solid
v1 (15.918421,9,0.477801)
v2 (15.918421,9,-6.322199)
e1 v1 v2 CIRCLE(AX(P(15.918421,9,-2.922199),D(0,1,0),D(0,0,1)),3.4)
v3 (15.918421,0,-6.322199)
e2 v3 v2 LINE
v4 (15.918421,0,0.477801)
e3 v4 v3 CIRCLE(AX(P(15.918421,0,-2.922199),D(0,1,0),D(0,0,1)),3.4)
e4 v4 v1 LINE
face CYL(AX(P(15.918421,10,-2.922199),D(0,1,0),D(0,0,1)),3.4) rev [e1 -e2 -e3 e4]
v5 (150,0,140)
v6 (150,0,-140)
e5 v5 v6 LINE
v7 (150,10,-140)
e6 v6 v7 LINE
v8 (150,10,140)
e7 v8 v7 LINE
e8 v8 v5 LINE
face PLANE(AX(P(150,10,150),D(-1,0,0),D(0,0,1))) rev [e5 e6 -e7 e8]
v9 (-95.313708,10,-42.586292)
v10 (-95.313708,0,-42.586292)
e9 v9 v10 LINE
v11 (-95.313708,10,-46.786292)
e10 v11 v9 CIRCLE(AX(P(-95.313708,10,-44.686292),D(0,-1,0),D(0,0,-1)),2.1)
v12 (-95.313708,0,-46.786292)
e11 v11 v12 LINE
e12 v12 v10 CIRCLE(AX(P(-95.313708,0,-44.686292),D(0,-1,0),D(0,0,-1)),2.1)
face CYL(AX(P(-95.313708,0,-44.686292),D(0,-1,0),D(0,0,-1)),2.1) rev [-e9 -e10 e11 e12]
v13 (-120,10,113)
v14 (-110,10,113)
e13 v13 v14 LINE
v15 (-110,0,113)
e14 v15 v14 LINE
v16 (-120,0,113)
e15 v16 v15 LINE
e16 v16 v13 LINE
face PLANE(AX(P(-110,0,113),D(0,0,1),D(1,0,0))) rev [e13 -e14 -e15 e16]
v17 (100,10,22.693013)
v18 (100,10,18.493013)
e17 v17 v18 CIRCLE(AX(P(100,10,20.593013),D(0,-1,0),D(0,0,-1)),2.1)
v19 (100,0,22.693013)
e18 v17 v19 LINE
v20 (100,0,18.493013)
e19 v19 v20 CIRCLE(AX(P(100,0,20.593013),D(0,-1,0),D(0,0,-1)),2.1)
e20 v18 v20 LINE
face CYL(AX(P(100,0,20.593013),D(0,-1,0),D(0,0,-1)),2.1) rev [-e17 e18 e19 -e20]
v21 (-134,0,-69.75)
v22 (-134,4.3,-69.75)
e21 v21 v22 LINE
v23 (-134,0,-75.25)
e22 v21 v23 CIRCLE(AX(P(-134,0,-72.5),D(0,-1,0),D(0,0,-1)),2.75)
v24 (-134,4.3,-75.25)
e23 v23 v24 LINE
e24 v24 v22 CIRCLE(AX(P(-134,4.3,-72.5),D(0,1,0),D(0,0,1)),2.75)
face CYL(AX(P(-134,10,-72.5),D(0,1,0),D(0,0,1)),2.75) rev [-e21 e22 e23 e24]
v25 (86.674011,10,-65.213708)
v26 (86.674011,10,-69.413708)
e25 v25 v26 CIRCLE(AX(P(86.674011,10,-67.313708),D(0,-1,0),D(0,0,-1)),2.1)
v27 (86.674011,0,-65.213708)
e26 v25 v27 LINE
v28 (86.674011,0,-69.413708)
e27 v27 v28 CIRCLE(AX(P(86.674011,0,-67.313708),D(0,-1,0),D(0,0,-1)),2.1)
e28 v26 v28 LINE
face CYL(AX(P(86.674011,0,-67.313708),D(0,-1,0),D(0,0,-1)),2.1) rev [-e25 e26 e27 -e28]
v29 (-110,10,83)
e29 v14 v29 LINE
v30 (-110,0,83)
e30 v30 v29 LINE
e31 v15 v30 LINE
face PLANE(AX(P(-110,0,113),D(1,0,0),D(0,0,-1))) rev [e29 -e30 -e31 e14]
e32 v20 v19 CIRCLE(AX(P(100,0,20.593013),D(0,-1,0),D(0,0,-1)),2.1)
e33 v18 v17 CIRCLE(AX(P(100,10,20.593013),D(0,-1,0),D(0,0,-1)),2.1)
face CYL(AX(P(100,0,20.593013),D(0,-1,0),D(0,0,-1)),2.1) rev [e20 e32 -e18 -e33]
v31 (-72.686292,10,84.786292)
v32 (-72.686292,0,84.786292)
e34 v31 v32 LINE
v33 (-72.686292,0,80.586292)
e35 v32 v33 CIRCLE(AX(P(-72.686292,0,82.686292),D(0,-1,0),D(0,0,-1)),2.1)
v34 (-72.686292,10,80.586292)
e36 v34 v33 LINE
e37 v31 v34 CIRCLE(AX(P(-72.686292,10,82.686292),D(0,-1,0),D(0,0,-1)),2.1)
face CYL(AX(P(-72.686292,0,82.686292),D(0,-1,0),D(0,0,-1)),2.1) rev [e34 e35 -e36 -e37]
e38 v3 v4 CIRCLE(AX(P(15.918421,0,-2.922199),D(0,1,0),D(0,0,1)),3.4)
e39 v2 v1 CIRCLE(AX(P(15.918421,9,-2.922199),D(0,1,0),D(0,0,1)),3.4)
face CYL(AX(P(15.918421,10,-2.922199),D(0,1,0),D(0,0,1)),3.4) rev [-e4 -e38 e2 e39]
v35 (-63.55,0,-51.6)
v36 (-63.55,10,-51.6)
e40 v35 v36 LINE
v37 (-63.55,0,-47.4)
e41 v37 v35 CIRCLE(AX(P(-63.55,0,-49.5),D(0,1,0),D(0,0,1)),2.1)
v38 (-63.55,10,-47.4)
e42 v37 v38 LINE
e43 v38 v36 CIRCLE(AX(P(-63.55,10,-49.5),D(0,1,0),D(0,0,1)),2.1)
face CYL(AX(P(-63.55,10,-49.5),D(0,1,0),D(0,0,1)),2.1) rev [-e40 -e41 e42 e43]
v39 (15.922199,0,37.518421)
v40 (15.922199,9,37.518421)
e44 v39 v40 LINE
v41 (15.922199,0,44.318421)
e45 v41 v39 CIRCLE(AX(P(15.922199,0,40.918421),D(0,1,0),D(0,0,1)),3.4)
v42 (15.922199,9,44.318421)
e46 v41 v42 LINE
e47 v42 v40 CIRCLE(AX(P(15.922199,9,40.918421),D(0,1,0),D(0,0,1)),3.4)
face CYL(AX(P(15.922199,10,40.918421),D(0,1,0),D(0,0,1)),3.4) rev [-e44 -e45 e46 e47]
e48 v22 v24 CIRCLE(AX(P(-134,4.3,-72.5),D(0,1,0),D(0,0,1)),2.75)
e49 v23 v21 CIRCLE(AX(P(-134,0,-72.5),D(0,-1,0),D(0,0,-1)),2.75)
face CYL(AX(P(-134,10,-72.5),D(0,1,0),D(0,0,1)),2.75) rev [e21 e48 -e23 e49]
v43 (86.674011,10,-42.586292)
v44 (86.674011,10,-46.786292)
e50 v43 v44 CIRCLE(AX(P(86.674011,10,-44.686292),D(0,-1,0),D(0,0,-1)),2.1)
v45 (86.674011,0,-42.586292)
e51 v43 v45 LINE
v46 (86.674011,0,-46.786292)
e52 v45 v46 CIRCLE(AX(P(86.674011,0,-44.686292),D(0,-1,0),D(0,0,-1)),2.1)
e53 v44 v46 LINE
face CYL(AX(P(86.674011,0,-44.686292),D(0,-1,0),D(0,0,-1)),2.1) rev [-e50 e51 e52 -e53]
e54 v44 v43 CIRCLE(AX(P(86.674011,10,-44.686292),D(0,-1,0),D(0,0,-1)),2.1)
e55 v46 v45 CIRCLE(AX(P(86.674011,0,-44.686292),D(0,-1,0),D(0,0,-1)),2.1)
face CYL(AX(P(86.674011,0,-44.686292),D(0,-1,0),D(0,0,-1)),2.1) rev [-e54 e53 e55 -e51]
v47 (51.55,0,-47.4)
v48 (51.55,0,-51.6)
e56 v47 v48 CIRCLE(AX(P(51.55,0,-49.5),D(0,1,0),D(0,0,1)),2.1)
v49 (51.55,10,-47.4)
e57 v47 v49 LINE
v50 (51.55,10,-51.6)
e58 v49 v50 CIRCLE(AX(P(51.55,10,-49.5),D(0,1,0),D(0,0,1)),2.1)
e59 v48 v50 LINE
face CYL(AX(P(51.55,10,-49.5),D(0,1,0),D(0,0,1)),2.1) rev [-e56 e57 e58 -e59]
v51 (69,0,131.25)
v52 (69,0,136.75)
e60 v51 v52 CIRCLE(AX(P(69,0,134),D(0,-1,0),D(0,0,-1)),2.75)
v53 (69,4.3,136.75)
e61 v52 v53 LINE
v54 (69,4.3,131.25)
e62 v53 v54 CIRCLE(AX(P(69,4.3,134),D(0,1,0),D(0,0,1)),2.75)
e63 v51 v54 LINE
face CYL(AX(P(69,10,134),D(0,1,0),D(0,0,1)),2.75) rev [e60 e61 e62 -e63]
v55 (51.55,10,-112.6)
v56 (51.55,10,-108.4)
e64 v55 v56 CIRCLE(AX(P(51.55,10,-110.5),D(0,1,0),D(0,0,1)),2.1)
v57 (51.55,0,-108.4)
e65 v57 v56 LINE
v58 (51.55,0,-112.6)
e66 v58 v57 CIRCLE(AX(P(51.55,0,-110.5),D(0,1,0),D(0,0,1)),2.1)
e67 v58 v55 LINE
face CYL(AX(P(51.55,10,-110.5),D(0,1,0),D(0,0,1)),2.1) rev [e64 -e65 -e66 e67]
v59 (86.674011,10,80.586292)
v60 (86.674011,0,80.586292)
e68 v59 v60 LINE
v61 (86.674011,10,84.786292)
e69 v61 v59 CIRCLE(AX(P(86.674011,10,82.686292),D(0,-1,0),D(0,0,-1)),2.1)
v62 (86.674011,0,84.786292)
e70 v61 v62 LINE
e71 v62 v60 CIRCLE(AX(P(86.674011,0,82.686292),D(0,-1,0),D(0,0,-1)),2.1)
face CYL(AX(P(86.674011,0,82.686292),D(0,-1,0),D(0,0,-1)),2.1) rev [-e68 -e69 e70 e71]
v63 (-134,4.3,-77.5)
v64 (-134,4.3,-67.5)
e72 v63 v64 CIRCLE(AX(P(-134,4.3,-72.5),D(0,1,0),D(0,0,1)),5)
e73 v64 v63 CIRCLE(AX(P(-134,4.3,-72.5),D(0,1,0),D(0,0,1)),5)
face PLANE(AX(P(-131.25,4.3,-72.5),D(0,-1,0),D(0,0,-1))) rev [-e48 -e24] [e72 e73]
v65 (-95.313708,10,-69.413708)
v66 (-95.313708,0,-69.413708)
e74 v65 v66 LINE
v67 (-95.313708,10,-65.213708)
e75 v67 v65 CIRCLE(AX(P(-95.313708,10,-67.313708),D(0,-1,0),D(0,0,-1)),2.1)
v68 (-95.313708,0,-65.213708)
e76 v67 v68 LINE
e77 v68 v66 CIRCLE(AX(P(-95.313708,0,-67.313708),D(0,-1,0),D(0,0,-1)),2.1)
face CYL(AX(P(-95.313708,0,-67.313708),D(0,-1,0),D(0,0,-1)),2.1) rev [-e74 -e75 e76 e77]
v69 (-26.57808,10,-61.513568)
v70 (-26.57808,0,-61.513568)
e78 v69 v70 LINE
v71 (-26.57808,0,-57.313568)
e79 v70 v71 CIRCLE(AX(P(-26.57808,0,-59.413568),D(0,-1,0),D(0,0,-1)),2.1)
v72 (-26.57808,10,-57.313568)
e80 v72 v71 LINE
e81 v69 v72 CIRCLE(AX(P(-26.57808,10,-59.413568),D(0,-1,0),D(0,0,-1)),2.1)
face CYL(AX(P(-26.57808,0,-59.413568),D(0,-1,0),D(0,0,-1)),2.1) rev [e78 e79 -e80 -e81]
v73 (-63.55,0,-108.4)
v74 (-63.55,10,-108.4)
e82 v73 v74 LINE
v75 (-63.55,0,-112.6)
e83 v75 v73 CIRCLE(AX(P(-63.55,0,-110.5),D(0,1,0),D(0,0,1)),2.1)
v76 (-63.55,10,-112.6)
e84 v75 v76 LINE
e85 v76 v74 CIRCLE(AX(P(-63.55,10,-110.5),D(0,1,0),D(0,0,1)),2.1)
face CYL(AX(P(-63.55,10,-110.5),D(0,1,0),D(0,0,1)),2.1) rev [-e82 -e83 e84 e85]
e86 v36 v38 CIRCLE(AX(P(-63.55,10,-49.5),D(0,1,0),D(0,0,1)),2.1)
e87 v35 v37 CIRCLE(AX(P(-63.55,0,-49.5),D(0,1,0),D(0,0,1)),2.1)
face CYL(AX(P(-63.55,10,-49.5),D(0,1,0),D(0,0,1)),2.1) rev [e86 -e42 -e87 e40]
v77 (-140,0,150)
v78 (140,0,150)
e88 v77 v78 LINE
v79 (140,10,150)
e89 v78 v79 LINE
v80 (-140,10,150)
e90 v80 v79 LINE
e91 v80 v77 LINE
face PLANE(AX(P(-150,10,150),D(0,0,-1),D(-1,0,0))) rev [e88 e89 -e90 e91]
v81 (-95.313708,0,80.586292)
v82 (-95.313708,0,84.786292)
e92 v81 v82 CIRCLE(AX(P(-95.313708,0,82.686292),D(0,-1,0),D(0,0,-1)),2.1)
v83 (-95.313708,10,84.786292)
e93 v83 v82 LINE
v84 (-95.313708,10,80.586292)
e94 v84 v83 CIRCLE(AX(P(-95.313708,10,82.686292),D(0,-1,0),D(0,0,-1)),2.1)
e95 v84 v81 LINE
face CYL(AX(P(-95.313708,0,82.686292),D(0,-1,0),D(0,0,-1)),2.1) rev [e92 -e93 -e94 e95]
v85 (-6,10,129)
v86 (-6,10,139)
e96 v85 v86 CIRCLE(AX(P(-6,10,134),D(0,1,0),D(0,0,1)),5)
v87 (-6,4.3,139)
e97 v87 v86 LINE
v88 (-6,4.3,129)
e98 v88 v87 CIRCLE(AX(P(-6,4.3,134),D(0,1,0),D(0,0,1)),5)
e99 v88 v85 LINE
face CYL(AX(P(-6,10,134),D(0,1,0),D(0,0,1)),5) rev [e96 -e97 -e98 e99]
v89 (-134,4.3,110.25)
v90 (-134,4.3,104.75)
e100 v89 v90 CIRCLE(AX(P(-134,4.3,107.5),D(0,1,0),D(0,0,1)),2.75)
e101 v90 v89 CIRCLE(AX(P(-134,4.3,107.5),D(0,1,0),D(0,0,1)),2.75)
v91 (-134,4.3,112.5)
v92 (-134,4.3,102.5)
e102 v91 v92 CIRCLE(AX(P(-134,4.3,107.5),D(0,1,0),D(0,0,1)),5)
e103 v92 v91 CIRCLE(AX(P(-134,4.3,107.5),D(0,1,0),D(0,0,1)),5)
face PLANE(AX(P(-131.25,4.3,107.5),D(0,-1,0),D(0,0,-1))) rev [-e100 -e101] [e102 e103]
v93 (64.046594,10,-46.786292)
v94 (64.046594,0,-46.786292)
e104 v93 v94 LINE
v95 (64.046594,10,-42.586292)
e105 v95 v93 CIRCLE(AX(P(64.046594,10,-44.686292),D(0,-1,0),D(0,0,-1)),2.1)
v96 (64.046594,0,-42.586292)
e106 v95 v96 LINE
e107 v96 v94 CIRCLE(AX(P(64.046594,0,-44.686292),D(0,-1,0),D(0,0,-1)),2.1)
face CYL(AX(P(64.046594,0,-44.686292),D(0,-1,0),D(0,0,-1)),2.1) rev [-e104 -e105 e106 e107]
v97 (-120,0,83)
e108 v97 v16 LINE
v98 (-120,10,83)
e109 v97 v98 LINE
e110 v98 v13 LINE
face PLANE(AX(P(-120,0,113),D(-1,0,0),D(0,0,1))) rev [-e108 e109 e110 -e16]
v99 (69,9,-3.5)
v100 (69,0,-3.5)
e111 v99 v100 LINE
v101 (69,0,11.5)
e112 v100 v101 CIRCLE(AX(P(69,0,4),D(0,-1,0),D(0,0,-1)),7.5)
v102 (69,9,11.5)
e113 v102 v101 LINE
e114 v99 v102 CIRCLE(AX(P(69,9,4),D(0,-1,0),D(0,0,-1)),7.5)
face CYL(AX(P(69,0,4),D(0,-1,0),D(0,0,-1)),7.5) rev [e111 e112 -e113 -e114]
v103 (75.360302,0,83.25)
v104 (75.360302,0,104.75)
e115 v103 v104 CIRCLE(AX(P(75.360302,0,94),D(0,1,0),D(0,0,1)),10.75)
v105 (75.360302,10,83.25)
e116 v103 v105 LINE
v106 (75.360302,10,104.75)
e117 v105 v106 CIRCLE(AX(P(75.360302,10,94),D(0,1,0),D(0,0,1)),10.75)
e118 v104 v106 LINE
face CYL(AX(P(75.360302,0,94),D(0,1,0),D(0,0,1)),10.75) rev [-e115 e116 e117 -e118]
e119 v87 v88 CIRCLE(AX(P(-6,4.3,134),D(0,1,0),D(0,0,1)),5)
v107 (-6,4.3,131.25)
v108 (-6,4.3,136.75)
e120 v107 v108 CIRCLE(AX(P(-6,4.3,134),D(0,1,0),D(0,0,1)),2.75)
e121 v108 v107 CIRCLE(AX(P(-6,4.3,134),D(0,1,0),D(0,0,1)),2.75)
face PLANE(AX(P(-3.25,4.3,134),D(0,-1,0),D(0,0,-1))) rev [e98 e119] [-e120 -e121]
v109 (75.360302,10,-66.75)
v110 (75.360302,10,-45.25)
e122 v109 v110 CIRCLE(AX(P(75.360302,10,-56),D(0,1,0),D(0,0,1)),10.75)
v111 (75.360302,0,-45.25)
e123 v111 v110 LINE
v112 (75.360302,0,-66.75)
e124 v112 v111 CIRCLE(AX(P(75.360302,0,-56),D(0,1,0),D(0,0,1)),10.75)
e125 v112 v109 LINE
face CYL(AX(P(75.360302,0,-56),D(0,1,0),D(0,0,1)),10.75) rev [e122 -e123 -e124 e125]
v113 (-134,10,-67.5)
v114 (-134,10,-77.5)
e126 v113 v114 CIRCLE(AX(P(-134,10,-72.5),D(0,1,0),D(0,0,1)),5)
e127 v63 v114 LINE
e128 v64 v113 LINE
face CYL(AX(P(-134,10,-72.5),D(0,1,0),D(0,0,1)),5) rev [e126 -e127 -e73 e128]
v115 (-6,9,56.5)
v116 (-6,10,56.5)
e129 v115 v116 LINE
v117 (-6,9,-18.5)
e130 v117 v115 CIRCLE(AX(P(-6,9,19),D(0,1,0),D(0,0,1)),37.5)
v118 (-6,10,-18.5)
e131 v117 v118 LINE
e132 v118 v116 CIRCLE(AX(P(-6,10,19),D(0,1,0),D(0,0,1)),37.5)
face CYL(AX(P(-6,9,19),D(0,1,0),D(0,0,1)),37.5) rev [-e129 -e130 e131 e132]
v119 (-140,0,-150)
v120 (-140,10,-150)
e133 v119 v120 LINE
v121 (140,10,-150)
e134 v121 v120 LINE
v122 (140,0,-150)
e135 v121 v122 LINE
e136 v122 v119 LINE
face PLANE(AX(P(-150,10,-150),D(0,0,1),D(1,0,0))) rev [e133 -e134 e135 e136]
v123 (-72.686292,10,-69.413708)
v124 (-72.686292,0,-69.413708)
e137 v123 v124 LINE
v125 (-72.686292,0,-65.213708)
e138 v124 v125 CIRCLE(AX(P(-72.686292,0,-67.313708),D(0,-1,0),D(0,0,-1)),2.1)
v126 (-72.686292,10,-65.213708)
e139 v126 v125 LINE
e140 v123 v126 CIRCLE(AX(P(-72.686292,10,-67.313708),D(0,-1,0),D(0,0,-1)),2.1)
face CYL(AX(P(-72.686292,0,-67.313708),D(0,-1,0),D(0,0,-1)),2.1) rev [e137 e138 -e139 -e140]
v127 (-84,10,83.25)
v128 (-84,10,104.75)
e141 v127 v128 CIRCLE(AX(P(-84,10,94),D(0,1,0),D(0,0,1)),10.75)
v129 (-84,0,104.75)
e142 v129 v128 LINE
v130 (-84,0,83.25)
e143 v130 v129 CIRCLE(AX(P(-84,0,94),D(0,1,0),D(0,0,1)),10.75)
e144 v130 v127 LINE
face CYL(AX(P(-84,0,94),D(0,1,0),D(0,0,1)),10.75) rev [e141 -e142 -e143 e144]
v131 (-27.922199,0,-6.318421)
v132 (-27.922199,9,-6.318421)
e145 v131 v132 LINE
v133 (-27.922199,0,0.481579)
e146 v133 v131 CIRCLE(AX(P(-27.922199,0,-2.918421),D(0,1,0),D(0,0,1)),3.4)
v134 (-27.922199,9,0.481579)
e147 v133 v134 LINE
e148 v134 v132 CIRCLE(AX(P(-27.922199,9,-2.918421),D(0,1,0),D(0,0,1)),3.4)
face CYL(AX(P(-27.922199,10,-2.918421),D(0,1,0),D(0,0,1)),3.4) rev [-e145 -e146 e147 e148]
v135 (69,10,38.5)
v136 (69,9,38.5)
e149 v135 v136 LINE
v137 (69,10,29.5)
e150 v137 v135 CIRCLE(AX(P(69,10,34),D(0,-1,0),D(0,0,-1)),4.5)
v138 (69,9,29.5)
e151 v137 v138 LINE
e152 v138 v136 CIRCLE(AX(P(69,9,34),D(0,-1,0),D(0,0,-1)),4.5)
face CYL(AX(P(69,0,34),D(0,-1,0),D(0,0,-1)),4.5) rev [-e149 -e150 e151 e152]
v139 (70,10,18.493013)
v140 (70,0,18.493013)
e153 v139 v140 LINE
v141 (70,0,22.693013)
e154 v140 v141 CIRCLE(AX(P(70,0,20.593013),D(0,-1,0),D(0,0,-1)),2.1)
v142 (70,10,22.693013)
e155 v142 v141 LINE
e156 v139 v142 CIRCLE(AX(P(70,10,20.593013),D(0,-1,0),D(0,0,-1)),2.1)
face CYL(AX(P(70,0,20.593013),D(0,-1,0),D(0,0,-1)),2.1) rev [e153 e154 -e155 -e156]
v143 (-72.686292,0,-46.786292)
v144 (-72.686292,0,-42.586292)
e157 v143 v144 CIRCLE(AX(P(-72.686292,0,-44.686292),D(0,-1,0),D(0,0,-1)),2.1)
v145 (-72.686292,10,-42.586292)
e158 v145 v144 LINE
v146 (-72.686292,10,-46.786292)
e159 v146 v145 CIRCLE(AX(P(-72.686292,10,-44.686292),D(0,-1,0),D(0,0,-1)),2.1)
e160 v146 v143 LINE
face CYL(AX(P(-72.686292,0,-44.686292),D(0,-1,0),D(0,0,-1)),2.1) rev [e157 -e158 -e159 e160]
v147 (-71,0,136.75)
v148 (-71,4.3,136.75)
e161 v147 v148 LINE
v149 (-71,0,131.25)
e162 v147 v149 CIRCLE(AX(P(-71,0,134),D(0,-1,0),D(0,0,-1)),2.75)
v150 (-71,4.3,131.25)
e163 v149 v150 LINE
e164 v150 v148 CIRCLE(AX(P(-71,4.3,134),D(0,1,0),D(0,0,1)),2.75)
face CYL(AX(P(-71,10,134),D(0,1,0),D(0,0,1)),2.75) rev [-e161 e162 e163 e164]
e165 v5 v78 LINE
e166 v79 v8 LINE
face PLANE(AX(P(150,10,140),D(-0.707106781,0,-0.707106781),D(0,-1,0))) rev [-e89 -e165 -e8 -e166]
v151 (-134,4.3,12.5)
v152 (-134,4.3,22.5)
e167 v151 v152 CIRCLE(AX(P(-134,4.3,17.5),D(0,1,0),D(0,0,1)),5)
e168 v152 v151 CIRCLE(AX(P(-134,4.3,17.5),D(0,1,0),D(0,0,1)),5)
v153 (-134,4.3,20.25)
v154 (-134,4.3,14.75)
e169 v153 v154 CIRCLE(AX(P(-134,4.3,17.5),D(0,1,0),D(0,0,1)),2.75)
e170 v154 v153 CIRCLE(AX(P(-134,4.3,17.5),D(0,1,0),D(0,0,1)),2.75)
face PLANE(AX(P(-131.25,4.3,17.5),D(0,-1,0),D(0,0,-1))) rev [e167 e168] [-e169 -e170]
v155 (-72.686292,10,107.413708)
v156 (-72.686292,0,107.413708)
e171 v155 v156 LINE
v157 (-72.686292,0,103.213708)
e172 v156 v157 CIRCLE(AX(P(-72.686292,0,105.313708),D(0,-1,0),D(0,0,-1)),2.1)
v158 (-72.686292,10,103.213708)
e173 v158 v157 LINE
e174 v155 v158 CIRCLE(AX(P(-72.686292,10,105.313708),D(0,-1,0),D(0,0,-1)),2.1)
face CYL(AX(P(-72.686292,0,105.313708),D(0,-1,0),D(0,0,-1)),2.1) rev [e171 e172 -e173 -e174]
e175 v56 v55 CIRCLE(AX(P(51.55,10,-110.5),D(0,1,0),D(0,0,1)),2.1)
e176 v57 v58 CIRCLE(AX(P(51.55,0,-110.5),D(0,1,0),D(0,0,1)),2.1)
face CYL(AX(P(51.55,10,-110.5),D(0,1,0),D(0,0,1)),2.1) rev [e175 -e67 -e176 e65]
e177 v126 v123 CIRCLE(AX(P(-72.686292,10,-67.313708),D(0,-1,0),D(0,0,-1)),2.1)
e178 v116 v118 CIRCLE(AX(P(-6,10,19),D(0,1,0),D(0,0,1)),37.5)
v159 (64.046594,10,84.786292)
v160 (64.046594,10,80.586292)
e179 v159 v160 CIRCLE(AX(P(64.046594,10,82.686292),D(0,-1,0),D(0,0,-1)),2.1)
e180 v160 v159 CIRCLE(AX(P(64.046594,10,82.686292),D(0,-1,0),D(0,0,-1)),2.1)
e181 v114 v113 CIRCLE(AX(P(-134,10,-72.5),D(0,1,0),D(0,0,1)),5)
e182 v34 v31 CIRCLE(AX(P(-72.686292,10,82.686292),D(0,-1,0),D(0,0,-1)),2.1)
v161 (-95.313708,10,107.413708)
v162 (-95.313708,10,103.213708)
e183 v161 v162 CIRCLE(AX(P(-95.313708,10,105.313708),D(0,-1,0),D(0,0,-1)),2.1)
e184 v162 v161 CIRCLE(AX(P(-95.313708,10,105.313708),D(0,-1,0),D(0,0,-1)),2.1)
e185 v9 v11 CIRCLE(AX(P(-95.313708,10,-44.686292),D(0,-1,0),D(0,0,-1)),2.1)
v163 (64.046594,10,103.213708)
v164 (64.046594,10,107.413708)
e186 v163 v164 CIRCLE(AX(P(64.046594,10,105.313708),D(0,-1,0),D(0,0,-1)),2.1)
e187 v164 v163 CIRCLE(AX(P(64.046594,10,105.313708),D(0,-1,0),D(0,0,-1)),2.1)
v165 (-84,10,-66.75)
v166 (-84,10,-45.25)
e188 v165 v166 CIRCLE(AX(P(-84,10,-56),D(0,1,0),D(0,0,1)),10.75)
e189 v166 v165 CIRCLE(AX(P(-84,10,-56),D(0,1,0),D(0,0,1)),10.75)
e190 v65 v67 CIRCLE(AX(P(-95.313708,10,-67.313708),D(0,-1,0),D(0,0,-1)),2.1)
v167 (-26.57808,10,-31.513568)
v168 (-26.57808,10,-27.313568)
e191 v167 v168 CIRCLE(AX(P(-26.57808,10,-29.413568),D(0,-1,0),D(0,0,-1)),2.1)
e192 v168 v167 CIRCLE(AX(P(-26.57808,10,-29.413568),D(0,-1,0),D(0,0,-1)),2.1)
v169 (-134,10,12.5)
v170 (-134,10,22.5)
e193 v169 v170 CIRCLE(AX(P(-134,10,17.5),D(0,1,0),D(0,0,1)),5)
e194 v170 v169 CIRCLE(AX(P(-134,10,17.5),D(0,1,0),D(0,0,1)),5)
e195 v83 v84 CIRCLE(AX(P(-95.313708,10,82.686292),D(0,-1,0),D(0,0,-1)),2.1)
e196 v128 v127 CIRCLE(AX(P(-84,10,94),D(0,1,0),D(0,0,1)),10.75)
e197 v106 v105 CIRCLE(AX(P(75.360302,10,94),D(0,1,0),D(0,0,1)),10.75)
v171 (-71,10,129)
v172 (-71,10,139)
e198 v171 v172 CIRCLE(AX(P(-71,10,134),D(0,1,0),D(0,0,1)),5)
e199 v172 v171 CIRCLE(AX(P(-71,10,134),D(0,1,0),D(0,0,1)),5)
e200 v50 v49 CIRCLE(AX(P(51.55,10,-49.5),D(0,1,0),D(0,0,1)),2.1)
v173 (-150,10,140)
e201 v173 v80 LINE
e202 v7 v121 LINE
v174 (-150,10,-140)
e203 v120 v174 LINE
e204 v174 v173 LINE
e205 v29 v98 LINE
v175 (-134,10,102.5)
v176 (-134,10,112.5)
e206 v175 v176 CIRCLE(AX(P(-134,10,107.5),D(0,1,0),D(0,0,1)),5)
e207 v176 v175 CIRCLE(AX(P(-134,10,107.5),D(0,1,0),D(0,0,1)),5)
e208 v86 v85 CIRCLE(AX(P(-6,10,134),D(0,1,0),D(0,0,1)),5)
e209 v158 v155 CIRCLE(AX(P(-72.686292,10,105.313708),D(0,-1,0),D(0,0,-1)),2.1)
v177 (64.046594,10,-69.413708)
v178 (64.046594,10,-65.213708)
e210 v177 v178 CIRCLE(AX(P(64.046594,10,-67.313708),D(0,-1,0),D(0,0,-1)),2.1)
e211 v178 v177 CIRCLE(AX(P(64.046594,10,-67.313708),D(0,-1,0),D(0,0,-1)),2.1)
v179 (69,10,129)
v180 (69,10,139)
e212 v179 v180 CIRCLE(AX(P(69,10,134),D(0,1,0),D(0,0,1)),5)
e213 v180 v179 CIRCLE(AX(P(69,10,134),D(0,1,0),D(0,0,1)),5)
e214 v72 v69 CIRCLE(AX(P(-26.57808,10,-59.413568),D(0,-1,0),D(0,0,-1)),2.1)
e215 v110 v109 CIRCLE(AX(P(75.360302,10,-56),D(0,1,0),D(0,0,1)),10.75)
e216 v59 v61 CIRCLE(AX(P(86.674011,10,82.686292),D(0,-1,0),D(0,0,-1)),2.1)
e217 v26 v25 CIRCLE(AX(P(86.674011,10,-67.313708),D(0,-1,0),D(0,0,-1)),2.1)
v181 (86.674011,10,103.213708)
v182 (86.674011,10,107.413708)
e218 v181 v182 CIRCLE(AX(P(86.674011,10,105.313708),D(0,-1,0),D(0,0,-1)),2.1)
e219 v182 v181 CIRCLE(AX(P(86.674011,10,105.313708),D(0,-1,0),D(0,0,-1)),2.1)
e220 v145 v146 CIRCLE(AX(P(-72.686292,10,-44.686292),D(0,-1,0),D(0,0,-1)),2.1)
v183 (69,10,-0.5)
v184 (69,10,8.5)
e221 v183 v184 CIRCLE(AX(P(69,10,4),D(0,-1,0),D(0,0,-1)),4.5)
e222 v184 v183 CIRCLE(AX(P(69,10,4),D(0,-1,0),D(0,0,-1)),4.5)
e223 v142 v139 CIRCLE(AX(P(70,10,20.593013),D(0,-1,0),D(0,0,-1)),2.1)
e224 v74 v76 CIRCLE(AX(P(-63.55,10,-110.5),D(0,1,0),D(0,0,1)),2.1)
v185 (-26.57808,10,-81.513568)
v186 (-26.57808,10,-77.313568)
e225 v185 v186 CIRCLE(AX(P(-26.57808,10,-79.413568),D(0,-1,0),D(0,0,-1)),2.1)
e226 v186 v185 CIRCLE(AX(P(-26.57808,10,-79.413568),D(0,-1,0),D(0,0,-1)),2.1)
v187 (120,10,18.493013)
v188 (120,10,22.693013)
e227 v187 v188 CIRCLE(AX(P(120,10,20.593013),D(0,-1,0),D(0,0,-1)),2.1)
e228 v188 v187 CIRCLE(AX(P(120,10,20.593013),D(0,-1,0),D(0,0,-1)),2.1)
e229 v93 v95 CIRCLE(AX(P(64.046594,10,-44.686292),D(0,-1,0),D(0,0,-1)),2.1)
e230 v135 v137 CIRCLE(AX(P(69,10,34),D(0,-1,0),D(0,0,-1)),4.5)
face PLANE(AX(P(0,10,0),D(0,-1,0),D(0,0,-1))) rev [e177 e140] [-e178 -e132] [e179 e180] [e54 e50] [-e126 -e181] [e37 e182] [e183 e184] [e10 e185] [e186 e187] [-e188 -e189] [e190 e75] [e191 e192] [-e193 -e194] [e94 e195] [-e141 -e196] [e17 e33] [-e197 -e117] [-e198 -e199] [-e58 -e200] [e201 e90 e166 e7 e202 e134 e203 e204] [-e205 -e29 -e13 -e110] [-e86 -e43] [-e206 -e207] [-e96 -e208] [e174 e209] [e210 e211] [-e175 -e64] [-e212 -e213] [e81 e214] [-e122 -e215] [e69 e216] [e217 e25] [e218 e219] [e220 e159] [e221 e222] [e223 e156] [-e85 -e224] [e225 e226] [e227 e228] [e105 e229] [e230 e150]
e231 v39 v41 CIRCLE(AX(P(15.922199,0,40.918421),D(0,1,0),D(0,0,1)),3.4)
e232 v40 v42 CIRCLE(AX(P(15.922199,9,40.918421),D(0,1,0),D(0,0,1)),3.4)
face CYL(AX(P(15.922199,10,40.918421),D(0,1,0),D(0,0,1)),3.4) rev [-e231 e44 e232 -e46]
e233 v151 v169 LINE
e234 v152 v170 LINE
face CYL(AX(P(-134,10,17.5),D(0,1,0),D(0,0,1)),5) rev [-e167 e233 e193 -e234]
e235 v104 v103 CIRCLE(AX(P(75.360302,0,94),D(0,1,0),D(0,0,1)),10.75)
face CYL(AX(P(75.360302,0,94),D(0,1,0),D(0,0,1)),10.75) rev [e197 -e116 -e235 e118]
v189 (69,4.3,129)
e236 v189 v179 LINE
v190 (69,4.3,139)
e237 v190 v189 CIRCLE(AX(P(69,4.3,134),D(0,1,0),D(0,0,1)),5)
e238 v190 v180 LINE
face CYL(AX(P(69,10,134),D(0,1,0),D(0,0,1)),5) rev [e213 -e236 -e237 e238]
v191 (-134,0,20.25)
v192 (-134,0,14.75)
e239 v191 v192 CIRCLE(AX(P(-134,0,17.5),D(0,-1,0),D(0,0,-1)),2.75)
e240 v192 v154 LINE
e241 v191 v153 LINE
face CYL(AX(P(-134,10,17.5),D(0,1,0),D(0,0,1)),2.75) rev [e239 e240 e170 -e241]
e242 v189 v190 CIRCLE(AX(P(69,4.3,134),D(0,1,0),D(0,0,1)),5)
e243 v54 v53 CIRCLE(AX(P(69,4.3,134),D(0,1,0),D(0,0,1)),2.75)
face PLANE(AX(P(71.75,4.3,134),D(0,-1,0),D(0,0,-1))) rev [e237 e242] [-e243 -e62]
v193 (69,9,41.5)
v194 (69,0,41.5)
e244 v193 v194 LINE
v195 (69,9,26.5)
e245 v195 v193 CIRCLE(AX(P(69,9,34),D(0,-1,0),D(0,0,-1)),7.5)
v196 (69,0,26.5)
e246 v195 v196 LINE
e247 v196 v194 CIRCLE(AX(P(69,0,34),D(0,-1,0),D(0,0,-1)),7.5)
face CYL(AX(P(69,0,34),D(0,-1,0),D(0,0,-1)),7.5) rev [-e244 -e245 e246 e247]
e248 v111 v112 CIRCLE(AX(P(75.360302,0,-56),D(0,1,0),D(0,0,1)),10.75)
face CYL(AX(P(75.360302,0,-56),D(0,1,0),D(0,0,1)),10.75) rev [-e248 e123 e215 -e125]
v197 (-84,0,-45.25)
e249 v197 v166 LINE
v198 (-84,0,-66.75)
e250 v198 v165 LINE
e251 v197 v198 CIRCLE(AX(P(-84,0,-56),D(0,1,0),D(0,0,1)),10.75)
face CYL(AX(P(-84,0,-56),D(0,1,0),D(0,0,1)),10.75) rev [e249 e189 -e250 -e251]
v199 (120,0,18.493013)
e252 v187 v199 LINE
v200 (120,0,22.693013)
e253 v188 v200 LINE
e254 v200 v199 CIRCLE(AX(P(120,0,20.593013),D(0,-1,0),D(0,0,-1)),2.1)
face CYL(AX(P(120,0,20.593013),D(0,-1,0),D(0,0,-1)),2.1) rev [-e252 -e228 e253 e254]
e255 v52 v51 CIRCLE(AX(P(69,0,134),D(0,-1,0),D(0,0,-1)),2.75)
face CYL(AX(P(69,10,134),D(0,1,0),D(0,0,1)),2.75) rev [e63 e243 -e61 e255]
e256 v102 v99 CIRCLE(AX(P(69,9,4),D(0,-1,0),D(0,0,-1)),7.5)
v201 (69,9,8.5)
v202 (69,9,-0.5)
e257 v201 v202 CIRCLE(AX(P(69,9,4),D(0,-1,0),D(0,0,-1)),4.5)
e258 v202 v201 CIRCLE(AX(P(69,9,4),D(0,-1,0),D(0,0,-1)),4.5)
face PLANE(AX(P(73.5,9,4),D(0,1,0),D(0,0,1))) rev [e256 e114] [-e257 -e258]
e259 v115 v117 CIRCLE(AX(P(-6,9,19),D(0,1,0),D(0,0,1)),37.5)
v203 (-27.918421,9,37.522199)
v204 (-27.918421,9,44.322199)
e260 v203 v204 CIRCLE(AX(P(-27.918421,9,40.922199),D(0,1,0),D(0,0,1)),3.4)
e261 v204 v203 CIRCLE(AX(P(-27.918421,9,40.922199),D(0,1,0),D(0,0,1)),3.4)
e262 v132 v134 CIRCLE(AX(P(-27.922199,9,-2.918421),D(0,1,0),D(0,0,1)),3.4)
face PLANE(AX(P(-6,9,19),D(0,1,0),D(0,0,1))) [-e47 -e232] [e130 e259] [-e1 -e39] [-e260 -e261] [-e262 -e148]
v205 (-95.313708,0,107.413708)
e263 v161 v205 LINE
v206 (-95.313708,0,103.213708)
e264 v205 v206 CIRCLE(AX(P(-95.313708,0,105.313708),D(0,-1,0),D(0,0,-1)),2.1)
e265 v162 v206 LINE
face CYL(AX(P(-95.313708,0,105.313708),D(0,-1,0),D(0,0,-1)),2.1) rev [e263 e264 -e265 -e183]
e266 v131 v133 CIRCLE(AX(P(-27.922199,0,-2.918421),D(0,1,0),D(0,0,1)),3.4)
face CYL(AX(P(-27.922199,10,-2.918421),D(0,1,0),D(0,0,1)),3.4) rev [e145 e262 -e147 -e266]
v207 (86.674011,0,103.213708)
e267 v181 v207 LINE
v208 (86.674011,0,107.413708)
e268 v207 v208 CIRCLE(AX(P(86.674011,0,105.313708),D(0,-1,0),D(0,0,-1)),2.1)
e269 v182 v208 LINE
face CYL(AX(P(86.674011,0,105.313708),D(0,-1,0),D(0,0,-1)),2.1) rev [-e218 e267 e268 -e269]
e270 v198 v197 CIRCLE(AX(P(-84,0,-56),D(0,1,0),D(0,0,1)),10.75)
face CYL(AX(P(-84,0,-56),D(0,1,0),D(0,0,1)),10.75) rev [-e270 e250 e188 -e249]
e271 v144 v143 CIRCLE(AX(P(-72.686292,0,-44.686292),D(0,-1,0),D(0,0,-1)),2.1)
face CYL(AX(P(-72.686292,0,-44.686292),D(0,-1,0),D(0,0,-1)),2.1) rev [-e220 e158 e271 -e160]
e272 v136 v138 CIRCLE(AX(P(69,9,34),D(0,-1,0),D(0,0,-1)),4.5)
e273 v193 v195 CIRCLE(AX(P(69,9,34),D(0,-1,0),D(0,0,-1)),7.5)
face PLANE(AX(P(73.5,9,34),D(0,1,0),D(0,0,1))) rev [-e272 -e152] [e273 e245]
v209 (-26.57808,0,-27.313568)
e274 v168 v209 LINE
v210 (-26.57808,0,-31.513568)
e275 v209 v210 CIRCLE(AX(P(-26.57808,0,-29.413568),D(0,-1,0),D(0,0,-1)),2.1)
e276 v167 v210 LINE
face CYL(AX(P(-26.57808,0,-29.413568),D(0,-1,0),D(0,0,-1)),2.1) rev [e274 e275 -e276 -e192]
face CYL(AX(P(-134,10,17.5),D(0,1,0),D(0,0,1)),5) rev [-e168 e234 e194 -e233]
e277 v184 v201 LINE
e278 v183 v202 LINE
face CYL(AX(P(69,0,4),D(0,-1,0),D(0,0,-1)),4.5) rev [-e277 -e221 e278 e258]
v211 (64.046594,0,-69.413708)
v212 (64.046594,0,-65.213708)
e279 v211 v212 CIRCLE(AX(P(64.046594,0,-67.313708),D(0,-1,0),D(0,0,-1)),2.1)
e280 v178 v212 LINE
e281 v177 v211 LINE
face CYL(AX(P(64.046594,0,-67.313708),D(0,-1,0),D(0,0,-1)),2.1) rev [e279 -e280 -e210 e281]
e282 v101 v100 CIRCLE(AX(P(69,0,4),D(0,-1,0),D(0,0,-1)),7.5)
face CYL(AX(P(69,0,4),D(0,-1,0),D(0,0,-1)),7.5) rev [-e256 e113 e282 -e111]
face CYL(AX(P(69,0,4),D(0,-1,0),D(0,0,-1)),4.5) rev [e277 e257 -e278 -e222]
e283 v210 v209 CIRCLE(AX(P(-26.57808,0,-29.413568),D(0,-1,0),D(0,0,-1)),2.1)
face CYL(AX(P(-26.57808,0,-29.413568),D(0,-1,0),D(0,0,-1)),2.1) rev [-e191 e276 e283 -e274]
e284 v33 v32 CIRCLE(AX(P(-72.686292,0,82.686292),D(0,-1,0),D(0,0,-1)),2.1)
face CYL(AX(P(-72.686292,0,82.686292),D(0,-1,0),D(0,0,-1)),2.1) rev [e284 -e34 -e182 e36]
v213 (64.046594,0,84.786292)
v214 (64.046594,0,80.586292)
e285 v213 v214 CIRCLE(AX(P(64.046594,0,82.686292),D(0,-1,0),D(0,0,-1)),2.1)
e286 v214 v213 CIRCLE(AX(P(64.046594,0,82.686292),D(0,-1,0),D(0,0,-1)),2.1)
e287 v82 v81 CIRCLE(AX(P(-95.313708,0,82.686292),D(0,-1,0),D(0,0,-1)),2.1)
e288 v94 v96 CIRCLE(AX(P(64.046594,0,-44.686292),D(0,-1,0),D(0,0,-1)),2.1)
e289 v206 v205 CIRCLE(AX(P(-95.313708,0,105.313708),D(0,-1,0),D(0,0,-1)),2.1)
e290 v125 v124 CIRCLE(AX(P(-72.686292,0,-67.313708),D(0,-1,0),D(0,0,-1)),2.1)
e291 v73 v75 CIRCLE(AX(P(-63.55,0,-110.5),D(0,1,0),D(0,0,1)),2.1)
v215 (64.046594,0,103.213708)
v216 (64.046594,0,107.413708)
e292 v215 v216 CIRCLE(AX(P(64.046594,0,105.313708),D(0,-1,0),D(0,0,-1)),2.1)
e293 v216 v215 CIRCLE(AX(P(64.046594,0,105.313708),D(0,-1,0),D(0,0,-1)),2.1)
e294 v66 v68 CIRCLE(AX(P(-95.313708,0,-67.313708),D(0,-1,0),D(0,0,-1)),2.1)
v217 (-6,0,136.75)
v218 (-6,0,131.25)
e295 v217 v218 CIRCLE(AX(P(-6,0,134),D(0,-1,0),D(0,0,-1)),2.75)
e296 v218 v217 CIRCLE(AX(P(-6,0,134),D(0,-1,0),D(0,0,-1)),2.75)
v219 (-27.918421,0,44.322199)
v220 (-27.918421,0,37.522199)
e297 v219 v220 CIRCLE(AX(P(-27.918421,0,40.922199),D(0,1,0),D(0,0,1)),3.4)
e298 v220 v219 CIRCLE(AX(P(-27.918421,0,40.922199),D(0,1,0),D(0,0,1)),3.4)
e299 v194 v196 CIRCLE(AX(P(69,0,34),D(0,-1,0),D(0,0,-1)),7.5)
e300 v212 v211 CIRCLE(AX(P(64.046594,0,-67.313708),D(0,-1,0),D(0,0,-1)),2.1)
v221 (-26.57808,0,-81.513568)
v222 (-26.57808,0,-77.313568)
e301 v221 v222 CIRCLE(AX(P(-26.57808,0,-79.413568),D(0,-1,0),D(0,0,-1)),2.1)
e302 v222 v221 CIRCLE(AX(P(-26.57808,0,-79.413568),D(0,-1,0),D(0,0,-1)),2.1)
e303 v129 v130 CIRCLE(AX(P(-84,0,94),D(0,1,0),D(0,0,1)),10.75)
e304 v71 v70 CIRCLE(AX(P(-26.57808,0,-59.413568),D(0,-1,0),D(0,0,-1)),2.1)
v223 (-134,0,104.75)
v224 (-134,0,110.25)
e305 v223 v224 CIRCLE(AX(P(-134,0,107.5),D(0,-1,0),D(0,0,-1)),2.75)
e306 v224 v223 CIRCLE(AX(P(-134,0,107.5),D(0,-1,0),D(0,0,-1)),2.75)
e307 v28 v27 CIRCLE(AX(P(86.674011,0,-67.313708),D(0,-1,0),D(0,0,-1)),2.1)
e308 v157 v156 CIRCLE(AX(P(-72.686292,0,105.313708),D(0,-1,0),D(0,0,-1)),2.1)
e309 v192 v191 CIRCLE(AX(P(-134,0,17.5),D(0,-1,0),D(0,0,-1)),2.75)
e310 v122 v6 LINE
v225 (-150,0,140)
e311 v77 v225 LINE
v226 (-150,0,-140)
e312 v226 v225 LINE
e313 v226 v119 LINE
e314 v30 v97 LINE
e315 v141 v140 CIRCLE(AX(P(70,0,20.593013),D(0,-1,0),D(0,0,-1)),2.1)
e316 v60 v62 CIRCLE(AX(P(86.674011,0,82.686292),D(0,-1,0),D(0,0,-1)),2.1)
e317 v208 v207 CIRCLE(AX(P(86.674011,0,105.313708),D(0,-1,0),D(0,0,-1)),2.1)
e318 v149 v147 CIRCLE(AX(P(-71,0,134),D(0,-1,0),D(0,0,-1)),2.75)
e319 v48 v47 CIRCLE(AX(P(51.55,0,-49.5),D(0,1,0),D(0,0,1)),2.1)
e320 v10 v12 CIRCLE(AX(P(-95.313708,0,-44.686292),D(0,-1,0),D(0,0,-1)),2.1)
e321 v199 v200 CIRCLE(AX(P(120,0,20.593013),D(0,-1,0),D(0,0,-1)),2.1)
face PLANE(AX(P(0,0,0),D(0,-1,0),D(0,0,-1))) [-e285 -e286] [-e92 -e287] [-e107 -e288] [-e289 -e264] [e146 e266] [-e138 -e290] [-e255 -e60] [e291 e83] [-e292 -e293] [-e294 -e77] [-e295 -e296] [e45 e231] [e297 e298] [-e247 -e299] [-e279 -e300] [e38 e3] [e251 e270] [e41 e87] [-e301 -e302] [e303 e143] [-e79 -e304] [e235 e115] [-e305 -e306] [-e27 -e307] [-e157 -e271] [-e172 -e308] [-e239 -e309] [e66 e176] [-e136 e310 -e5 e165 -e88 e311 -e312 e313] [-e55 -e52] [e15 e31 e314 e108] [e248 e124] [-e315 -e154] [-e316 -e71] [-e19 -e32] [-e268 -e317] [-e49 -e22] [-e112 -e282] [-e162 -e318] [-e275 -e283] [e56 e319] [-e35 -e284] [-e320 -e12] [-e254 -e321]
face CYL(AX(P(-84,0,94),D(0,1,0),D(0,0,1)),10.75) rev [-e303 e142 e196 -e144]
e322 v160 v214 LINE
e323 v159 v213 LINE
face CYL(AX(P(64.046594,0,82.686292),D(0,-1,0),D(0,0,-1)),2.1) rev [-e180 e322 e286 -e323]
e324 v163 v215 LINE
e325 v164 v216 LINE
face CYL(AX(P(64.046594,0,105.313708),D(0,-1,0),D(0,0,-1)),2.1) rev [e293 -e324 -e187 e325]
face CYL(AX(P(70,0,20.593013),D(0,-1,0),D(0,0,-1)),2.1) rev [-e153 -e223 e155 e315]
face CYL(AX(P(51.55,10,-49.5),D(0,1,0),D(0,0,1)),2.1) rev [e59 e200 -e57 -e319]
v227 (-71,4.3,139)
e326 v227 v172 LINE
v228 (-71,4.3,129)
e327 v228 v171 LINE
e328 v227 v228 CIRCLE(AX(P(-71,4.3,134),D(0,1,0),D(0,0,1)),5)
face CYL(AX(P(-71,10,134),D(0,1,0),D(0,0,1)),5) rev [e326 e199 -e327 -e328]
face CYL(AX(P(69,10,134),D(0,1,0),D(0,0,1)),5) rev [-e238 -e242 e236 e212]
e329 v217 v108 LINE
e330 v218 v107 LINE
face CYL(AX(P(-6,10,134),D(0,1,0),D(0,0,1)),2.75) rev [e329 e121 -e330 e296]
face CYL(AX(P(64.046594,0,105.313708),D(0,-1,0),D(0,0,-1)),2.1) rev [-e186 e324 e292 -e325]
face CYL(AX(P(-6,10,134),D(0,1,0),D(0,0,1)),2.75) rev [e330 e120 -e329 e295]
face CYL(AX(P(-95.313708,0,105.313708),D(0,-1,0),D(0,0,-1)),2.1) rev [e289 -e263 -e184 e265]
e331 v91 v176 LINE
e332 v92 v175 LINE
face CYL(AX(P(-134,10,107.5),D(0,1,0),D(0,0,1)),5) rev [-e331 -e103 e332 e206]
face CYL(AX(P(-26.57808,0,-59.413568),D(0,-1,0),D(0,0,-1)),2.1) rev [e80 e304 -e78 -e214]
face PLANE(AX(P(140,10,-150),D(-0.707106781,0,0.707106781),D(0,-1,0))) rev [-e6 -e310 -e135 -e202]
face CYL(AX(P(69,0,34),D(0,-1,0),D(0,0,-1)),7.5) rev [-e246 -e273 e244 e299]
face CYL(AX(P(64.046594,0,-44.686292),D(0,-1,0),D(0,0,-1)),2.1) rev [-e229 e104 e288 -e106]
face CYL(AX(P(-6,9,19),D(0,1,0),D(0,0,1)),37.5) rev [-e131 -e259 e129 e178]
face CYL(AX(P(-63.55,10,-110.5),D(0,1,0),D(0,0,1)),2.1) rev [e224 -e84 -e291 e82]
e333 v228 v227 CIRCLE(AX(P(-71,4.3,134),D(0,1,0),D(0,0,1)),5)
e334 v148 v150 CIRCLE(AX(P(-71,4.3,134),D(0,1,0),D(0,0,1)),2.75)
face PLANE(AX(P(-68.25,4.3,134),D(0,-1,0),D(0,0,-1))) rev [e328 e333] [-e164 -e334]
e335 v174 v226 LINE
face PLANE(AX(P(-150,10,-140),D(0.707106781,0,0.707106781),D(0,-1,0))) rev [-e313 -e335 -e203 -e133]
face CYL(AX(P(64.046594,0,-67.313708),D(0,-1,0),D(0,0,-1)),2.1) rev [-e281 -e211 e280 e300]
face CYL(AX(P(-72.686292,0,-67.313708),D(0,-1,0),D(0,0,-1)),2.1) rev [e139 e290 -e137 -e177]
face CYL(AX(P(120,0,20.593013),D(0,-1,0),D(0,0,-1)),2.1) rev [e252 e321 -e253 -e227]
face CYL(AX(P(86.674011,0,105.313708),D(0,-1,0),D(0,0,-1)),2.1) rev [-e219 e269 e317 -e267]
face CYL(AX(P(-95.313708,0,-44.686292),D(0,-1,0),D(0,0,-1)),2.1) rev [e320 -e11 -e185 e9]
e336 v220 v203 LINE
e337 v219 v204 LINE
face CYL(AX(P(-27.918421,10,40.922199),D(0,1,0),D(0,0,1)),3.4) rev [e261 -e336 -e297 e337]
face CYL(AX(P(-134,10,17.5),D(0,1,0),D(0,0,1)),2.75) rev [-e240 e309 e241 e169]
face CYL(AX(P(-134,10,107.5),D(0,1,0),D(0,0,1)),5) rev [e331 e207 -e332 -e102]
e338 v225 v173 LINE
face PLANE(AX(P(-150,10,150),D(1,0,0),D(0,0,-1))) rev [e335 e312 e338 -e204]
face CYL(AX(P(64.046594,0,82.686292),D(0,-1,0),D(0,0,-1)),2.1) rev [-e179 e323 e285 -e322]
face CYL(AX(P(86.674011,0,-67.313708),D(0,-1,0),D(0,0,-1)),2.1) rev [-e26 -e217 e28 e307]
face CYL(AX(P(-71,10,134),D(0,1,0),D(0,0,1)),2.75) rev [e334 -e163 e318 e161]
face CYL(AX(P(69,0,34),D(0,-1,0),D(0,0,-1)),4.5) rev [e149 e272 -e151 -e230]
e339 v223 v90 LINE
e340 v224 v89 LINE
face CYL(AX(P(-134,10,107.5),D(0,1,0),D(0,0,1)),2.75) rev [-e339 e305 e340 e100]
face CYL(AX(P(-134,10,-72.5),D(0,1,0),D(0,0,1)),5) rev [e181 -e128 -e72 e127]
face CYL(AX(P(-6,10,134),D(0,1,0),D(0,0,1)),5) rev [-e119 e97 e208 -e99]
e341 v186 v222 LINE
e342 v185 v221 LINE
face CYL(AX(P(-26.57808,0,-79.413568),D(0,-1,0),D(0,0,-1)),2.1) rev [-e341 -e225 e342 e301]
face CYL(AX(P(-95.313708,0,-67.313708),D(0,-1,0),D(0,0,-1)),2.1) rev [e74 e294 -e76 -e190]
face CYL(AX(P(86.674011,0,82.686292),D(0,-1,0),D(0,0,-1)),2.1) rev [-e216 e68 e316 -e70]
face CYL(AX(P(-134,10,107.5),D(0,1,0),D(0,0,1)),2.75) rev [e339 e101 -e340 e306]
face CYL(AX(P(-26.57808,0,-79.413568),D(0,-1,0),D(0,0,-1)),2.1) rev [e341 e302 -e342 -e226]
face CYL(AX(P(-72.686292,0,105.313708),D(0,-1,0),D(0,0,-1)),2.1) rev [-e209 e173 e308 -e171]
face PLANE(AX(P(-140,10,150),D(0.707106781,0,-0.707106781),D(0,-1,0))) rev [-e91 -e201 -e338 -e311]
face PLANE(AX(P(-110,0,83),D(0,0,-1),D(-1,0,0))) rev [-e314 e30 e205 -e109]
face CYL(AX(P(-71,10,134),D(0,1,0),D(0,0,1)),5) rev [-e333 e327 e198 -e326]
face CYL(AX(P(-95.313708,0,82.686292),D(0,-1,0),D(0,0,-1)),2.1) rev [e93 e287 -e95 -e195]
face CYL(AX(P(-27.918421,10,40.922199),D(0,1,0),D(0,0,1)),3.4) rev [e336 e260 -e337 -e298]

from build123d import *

# Parameters (mm, degrees)
SKETCH1_W                                            = 300
SKETCH1_H                                            = 300
BOSS_EXTRUDE1_DEPTH                                  = 10
SKETCH2_R                                            = 37.5
CUT_EXTRUDE1_DEPTH                                   = 1
SKETCH3_W                                            = 10
SKETCH3_H                                            = 30
CUT_EXTRUDE2_DEPTH                                   = 213.367605816
SKETCH4_R                                            = 10.75
CUT_EXTRUDE3_DEPTH                                   = 213.367605816
CBORE_FOR_M8_HEXAGON_SOCKET_HEAD_CAP_SCR_D           = 9
CBORE_FOR_M8_HEXAGON_SOCKET_HEAD_CAP_SCR_CBORE_D     = 15
CBORE_FOR_M8_HEXAGON_SOCKET_HEAD_CAP_SCR_CBORE_DEPTH = 9
M8_TAPPED_HOLE1_D                                    = 6.8
M5_TAPPED_HOLE1_D                                    = 4.2
M5_TAPPED_HOLE2_D                                    = 4.2
CHAMFER1_SIZE                                        = 10
M5_TAPPED_HOLE3_D                                    = 4.2
M5_TAPPED_HOLE3_DEPTH                                = 36.9
M5_TAPPED_HOLE3_TIP                                  = 1.2618073
CBORE_FOR_M5_HEXAGON_SOCKET_HEAD_CAP_SCR_D           = 5.5
CBORE_FOR_M5_HEXAGON_SOCKET_HEAD_CAP_SCR_DEPTH       = 36.9
CBORE_FOR_M5_HEXAGON_SOCKET_HEAD_CAP_SCR_CBORE_D     = 10
CBORE_FOR_M5_HEXAGON_SOCKET_HEAD_CAP_SCR_CBORE_DEPTH = 5.7
CBORE_FOR_M5_HEXAGON_SOCKET_HEAD_CAP_SCR_TIP         = 1.652366702


with BuildPart() as part:
    # Sketch1 → Boss-Extrude1 (new body)
    with BuildSketch(Plane(origin=(0, 0, 0), x_dir=(1, 0, 0), z_dir=(0, 1, 0))):
        Rectangle(SKETCH1_W, SKETCH1_H)
    extrude(amount=BOSS_EXTRUDE1_DEPTH)

    # Sketch2 → Cut-Extrude1 (cut)
    with BuildSketch(Plane(origin=(0, 10, 0), x_dir=(1, 0, 0), z_dir=(0, 1, 0))):
        with Locations(Location((-6, -19, 0), (0, 0, 270))):
            Circle(SKETCH2_R)
    extrude(amount=-CUT_EXTRUDE1_DEPTH, mode=Mode.SUBTRACT)

    # Sketch3 → Cut-Extrude2 (cut, through all)
    with BuildSketch(Plane(origin=(0, 10, 0), x_dir=(1, 0, 0), z_dir=(0, 1, 0))):
        with Locations((-115, -98)):
            Rectangle(SKETCH3_W, SKETCH3_H)
    extrude(amount=-CUT_EXTRUDE2_DEPTH, mode=Mode.SUBTRACT)

    # Sketch4 → Cut-Extrude3 (cut, through all)
    with BuildSketch(Plane(origin=(0, 10, 0), x_dir=(1, 0, 0), z_dir=(0, 1, 0))):
        with Locations(Location((-84, -94, 0), (0, 0, 270))):
            Circle(SKETCH4_R)
        with Locations(Location((-84, 56, 0), (0, 0, 270))):
            Circle(SKETCH4_R)
        with Locations(Location((75.36030205, 56, 0), (0, 0, 270))):
            Circle(SKETCH4_R)
        with Locations(Location((75.36030205, -94, 0), (0, 0, 270))):
            Circle(SKETCH4_R)
    extrude(amount=-CUT_EXTRUDE3_DEPTH, mode=Mode.SUBTRACT)

    # CBORE for M8 Hexagon socket head cap screws1 (through all)
    with Locations(Plane(origin=(0, 0, 0), x_dir=(-1, 0, 0), z_dir=(0, -1, 0))):
        with Locations((-69, -4), (-69, -34)):
            CounterBoreHole(CBORE_FOR_M8_HEXAGON_SOCKET_HEAD_CAP_SCR_D / 2, CBORE_FOR_M8_HEXAGON_SOCKET_HEAD_CAP_SCR_CBORE_D / 2, CBORE_FOR_M8_HEXAGON_SOCKET_HEAD_CAP_SCR_CBORE_DEPTH)

    # M8 Tapped Hole1 (through all)
    with Locations(Plane(origin=(0, 10, 0), x_dir=(1, 0, 0), z_dir=(0, 1, 0))):
        with Locations((15.922198881, -40.918421389), (15.918421389, 2.922198881), (-27.922198881, 2.918421389), (-27.918421389, -40.922198881)):
            Hole(M8_TAPPED_HOLE1_D / 2)

    # M5 Tapped Hole1 (through all)
    with Locations(Plane(origin=(0, 0, 0), x_dir=(-1, 0, 0), z_dir=(0, -1, 0))):
        with Locations((72.686291501, 44.686291501), (95.313708499, 44.686291501), (95.313708499, 67.313708499), (72.686291501, 67.313708499), (95.313708499, -82.686291501), (95.313708499, -105.313708499), (72.686291501, -105.313708499), (72.686291501, -82.686291501), (-64.046593551, -82.686291501), (-64.046593551, -105.313708499), (-86.674010549, -105.313708499), (-86.674010549, -82.686291501), (-64.046593551, 67.313708499), (-64.046593551, 44.686291501), (-86.674010549, 44.686291501), (-86.674010549, 67.313708499)):
            Hole(M5_TAPPED_HOLE1_D / 2)

    # M5 Tapped Hole2 (through all)
    with Locations(Plane(origin=(0, 10, 0), x_dir=(1, 0, 0), z_dir=(0, 1, 0))):
        with Locations((51.55, 110.5), (-63.55, 110.5), (-63.55, 49.5), (51.55, 49.5)):
            Hole(M5_TAPPED_HOLE2_D / 2)

    # Chamfer1
    chamfer1_edges = [part.edges().sort_by_distance(p)[0] for p in [
        (150, 5, 150),
        (-150, 5, 150),
        (-150, 5, -150),
        (150, 5, -150),
    ]]
    chamfer(chamfer1_edges, length=CHAMFER1_SIZE)

    # M5 Tapped Hole3
    with Locations(Plane(origin=(0, 0, 0), x_dir=(-1, 0, 0), z_dir=(0, -1, 0))):
        with Locations((26.578080425, 59.413568319), (-100, -20.593013208), (26.578080425, 79.413568319), (26.578080425, 29.413568319), (-120, -20.593013208), (-70, -20.593013208)):
            Hole(M5_TAPPED_HOLE3_D / 2, depth=M5_TAPPED_HOLE3_DEPTH)
            with Locations((0, 0, -(M5_TAPPED_HOLE3_DEPTH + M5_TAPPED_HOLE3_TIP / 2))):  # 118° drill point
                Cone(0, M5_TAPPED_HOLE3_D / 2, M5_TAPPED_HOLE3_TIP, mode=Mode.SUBTRACT)

    # CBORE for M5 Hexagon socket head cap screws1
    with Locations(Plane(origin=(0, 10, 0), x_dir=(1, 0, 0), z_dir=(0, 1, 0))):
        with Locations((-134, -107.5), (-71, -134), (-6, -134), (69, -134), (-134, 72.5), (-134, -17.5)):
            CounterBoreHole(CBORE_FOR_M5_HEXAGON_SOCKET_HEAD_CAP_SCR_D / 2, CBORE_FOR_M5_HEXAGON_SOCKET_HEAD_CAP_SCR_CBORE_D / 2, CBORE_FOR_M5_HEXAGON_SOCKET_HEAD_CAP_SCR_CBORE_DEPTH, depth=CBORE_FOR_M5_HEXAGON_SOCKET_HEAD_CAP_SCR_DEPTH)
            with Locations((0, 0, -(CBORE_FOR_M5_HEXAGON_SOCKET_HEAD_CAP_SCR_DEPTH + CBORE_FOR_M5_HEXAGON_SOCKET_HEAD_CAP_SCR_TIP / 2))):  # 118° drill point
                Cone(0, CBORE_FOR_M5_HEXAGON_SOCKET_HEAD_CAP_SCR_D / 2, CBORE_FOR_M5_HEXAGON_SOCKET_HEAD_CAP_SCR_TIP, mode=Mode.SUBTRACT)


solid = part.part
